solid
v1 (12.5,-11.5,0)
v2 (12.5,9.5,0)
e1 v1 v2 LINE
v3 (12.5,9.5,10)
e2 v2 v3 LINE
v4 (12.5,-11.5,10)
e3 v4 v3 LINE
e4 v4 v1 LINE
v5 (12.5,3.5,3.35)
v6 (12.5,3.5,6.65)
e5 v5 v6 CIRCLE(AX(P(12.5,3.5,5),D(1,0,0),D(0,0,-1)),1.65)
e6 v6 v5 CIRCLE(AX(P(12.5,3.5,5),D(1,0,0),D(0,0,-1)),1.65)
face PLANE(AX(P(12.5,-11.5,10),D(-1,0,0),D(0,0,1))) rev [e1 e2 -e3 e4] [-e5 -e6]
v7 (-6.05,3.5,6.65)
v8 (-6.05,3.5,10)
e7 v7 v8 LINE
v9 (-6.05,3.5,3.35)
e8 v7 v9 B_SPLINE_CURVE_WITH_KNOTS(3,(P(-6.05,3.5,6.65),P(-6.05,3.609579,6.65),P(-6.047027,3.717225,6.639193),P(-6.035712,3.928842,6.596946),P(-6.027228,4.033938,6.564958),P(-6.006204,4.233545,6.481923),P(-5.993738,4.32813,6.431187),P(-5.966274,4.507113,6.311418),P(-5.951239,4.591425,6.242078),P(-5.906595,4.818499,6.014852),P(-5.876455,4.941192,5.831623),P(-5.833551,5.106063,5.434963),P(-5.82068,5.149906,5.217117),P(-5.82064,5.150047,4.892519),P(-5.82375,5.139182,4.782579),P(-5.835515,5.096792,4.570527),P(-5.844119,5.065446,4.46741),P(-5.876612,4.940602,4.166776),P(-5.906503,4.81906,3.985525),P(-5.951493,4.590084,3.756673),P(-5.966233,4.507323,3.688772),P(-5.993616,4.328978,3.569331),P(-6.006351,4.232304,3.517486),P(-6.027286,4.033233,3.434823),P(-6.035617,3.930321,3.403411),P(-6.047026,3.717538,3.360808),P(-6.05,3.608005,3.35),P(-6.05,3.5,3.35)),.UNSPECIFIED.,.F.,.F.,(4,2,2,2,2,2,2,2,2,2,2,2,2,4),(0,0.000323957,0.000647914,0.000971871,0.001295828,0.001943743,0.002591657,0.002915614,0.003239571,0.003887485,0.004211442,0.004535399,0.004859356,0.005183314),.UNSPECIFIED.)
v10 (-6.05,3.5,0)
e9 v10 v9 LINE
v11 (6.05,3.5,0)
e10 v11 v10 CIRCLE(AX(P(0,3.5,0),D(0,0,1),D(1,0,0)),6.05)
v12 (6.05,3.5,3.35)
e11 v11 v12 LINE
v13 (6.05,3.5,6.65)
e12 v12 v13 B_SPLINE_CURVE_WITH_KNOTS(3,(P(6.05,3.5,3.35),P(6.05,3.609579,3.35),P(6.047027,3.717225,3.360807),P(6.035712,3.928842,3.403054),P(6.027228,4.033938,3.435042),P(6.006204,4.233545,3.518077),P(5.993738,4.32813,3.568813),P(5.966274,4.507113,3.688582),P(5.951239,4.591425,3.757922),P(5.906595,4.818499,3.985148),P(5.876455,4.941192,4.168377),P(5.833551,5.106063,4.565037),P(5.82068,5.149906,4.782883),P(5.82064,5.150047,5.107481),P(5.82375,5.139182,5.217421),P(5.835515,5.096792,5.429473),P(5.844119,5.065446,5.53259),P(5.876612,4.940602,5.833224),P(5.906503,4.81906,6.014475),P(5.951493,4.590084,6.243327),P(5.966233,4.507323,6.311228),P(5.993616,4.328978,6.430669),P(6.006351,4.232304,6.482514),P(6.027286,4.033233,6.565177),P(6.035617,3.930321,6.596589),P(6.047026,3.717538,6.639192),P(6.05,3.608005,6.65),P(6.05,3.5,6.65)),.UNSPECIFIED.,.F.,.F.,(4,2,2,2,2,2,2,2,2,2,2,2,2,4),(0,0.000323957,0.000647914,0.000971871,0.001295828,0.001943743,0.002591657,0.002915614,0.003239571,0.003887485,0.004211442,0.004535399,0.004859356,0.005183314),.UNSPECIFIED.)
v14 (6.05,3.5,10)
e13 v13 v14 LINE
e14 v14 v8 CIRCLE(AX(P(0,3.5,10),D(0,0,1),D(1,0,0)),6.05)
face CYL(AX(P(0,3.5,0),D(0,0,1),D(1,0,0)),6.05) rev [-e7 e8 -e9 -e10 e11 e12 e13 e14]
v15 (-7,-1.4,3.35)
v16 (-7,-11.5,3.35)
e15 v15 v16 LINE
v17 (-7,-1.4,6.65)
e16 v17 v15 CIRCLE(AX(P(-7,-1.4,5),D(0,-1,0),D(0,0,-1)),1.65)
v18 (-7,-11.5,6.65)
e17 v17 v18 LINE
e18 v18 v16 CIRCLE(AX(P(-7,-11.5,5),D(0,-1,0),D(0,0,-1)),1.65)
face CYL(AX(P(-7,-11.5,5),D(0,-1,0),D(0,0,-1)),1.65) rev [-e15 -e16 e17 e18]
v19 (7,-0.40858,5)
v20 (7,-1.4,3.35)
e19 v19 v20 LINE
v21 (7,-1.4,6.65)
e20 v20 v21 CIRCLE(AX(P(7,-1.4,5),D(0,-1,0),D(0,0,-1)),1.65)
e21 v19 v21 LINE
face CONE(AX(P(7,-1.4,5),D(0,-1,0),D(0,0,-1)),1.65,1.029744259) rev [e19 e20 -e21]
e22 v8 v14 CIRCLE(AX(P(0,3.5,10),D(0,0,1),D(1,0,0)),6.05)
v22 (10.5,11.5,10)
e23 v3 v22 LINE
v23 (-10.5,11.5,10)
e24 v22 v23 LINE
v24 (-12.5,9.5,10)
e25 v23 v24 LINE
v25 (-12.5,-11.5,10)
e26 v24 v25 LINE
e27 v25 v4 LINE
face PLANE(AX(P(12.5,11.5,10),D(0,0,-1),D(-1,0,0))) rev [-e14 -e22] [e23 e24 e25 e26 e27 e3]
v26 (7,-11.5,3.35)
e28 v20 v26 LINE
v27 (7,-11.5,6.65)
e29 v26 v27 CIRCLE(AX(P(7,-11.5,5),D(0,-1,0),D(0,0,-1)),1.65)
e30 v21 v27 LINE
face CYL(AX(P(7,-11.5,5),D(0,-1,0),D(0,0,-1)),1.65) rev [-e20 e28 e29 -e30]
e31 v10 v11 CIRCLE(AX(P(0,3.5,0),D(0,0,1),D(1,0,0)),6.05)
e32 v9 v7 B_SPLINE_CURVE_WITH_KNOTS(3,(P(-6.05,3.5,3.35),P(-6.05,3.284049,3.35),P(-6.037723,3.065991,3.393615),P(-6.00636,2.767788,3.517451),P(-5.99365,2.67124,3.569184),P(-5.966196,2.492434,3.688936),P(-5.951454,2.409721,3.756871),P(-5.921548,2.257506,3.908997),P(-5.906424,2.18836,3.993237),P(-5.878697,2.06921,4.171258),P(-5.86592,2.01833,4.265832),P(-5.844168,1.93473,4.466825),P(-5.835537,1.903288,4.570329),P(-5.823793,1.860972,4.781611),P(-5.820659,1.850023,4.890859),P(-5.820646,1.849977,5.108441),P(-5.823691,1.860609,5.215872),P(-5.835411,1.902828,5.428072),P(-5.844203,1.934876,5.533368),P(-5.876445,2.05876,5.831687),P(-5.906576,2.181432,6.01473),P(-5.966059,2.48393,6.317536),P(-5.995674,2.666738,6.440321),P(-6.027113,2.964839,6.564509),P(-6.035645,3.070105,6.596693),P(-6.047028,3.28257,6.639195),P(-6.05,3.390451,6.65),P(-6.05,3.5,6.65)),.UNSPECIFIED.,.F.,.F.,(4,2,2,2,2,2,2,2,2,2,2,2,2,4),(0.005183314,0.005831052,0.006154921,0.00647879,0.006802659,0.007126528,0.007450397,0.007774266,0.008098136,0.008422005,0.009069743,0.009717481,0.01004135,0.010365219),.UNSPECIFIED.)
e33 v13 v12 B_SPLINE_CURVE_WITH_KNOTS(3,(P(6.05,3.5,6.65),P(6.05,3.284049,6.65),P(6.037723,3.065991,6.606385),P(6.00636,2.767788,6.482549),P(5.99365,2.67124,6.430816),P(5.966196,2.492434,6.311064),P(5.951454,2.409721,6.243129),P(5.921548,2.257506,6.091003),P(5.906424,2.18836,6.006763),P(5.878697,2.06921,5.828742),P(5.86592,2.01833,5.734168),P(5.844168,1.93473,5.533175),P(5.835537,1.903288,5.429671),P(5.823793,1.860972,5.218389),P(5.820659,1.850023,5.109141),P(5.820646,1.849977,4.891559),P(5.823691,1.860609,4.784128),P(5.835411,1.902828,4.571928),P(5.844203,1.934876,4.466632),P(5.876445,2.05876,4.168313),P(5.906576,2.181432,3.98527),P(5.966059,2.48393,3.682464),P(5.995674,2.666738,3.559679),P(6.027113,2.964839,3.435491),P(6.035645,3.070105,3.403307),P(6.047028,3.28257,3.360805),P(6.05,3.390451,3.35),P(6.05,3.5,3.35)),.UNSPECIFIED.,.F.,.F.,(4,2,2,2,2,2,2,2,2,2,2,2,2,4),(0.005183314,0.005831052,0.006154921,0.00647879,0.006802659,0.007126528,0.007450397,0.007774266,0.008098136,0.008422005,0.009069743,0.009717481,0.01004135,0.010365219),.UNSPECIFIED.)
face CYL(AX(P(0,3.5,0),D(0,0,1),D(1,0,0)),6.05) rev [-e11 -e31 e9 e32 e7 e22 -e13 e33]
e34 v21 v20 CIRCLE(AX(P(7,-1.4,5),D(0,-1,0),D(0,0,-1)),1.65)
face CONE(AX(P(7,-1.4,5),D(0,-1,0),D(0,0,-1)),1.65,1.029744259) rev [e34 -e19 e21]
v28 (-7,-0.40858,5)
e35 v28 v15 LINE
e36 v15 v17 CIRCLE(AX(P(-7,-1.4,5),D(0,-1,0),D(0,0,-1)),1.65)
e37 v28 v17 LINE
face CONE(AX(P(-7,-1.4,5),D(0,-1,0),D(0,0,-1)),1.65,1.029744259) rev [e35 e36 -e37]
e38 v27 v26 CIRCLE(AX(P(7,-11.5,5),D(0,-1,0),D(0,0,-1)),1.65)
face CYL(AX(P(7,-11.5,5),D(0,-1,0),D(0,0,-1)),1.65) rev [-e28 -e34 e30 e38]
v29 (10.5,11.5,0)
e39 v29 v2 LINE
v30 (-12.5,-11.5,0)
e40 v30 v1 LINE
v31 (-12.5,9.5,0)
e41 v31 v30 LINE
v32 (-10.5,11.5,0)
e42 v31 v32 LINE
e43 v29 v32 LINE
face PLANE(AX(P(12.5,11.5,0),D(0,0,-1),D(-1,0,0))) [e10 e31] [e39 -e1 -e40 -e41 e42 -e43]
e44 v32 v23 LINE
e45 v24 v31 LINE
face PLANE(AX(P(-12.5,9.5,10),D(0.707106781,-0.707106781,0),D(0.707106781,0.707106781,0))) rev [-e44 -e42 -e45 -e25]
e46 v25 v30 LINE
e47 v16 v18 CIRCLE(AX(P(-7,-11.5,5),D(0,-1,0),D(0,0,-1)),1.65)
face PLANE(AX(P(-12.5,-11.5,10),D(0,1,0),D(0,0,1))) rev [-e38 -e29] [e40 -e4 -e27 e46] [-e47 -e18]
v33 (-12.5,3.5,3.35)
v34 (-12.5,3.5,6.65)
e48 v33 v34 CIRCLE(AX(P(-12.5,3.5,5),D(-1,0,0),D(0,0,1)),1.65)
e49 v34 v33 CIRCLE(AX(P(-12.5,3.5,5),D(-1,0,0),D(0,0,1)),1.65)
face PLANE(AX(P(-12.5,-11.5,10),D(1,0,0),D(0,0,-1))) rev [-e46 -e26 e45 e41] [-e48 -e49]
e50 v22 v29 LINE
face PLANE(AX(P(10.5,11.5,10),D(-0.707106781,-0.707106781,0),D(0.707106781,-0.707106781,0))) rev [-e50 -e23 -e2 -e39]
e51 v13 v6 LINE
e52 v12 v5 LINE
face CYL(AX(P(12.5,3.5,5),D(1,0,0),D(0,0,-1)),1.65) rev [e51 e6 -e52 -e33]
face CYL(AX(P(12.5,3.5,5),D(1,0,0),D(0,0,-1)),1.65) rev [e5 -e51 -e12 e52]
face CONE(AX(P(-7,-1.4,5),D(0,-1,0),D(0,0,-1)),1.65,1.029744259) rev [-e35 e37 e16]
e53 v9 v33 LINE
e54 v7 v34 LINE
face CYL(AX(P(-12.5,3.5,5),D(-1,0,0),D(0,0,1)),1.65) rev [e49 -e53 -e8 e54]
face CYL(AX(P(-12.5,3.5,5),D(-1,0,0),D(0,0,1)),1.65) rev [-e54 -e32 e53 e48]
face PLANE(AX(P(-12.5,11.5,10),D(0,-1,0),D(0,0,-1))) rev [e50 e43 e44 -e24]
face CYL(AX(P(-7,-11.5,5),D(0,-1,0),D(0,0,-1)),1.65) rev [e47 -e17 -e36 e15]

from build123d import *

# Parameters (mm, degrees)
SKETCH1_W             = 25
SKETCH1_H             = 23
BOSS_EXTRUDE1_DEPTH   = 10
SKETCH2_R             = 6.05
CUT_EXTRUDE1_DEPTH    = 20.710403344
CHAMFER1_SIZE         = 2
M4_TAPPED_HOLE1_D     = 3.3
M4_TAPPED_HOLE1_DEPTH = 10.1
M4_TAPPED_HOLE1_TIP   = 0.991420021


with BuildPart() as part:
    # Sketch1 → Boss-Extrude1 (new body)
    with BuildSketch(Plane.XY):
        Rectangle(SKETCH1_W, SKETCH1_H)
    extrude(amount=BOSS_EXTRUDE1_DEPTH)

    # Sketch2 → Cut-Extrude1 (cut, through all)
    with BuildSketch(Plane.XY.offset(10)):
        with Locations((0, 3.5)):
            Circle(SKETCH2_R)
    extrude(amount=-CUT_EXTRUDE1_DEPTH, mode=Mode.SUBTRACT)

    # Chamfer1
    chamfer1_edges = [part.edges().sort_by_distance(p)[0] for p in [
        (-12.5, 11.5, 5),
        (12.5, 11.5, 5),
    ]]
    chamfer(chamfer1_edges, length=CHAMFER1_SIZE)

    # M4 Tapped Hole1
    with Locations(Plane.XZ.offset(11.5)):
        with Locations((-7, 5), (7, 5)):
            Hole(M4_TAPPED_HOLE1_D / 2, depth=M4_TAPPED_HOLE1_DEPTH)
            with Locations((0, 0, -(M4_TAPPED_HOLE1_DEPTH + M4_TAPPED_HOLE1_TIP / 2))):  # 118° drill point
                Cone(0, M4_TAPPED_HOLE1_D / 2, M4_TAPPED_HOLE1_TIP, mode=Mode.SUBTRACT)

    # Sketch5 → M4 Tapped Hole2 (revolve, cut)
    with BuildSketch(Plane(origin=(-12.5, 3.5, 5), x_dir=(0, 0, 1), z_dir=(0, 1, 0))):
        Polygon((0, 0), (0, 11.091420021), (1.65, 10.1), (1.65, 0), align=None)
    m4_tapped_hole2 = revolve(axis=Axis((-18.85, 3.5, 5), (1, 0, 0)), mode=Mode.SUBTRACT)

    # Mirror1: M4 Tapped Hole2 across plane
    add(m4_tapped_hole2.mirror(Plane(origin=(0, 0, 0), x_dir=(0, 0, 1), z_dir=(1, 0, 0))), mode=Mode.SUBTRACT)


solid = part.part
